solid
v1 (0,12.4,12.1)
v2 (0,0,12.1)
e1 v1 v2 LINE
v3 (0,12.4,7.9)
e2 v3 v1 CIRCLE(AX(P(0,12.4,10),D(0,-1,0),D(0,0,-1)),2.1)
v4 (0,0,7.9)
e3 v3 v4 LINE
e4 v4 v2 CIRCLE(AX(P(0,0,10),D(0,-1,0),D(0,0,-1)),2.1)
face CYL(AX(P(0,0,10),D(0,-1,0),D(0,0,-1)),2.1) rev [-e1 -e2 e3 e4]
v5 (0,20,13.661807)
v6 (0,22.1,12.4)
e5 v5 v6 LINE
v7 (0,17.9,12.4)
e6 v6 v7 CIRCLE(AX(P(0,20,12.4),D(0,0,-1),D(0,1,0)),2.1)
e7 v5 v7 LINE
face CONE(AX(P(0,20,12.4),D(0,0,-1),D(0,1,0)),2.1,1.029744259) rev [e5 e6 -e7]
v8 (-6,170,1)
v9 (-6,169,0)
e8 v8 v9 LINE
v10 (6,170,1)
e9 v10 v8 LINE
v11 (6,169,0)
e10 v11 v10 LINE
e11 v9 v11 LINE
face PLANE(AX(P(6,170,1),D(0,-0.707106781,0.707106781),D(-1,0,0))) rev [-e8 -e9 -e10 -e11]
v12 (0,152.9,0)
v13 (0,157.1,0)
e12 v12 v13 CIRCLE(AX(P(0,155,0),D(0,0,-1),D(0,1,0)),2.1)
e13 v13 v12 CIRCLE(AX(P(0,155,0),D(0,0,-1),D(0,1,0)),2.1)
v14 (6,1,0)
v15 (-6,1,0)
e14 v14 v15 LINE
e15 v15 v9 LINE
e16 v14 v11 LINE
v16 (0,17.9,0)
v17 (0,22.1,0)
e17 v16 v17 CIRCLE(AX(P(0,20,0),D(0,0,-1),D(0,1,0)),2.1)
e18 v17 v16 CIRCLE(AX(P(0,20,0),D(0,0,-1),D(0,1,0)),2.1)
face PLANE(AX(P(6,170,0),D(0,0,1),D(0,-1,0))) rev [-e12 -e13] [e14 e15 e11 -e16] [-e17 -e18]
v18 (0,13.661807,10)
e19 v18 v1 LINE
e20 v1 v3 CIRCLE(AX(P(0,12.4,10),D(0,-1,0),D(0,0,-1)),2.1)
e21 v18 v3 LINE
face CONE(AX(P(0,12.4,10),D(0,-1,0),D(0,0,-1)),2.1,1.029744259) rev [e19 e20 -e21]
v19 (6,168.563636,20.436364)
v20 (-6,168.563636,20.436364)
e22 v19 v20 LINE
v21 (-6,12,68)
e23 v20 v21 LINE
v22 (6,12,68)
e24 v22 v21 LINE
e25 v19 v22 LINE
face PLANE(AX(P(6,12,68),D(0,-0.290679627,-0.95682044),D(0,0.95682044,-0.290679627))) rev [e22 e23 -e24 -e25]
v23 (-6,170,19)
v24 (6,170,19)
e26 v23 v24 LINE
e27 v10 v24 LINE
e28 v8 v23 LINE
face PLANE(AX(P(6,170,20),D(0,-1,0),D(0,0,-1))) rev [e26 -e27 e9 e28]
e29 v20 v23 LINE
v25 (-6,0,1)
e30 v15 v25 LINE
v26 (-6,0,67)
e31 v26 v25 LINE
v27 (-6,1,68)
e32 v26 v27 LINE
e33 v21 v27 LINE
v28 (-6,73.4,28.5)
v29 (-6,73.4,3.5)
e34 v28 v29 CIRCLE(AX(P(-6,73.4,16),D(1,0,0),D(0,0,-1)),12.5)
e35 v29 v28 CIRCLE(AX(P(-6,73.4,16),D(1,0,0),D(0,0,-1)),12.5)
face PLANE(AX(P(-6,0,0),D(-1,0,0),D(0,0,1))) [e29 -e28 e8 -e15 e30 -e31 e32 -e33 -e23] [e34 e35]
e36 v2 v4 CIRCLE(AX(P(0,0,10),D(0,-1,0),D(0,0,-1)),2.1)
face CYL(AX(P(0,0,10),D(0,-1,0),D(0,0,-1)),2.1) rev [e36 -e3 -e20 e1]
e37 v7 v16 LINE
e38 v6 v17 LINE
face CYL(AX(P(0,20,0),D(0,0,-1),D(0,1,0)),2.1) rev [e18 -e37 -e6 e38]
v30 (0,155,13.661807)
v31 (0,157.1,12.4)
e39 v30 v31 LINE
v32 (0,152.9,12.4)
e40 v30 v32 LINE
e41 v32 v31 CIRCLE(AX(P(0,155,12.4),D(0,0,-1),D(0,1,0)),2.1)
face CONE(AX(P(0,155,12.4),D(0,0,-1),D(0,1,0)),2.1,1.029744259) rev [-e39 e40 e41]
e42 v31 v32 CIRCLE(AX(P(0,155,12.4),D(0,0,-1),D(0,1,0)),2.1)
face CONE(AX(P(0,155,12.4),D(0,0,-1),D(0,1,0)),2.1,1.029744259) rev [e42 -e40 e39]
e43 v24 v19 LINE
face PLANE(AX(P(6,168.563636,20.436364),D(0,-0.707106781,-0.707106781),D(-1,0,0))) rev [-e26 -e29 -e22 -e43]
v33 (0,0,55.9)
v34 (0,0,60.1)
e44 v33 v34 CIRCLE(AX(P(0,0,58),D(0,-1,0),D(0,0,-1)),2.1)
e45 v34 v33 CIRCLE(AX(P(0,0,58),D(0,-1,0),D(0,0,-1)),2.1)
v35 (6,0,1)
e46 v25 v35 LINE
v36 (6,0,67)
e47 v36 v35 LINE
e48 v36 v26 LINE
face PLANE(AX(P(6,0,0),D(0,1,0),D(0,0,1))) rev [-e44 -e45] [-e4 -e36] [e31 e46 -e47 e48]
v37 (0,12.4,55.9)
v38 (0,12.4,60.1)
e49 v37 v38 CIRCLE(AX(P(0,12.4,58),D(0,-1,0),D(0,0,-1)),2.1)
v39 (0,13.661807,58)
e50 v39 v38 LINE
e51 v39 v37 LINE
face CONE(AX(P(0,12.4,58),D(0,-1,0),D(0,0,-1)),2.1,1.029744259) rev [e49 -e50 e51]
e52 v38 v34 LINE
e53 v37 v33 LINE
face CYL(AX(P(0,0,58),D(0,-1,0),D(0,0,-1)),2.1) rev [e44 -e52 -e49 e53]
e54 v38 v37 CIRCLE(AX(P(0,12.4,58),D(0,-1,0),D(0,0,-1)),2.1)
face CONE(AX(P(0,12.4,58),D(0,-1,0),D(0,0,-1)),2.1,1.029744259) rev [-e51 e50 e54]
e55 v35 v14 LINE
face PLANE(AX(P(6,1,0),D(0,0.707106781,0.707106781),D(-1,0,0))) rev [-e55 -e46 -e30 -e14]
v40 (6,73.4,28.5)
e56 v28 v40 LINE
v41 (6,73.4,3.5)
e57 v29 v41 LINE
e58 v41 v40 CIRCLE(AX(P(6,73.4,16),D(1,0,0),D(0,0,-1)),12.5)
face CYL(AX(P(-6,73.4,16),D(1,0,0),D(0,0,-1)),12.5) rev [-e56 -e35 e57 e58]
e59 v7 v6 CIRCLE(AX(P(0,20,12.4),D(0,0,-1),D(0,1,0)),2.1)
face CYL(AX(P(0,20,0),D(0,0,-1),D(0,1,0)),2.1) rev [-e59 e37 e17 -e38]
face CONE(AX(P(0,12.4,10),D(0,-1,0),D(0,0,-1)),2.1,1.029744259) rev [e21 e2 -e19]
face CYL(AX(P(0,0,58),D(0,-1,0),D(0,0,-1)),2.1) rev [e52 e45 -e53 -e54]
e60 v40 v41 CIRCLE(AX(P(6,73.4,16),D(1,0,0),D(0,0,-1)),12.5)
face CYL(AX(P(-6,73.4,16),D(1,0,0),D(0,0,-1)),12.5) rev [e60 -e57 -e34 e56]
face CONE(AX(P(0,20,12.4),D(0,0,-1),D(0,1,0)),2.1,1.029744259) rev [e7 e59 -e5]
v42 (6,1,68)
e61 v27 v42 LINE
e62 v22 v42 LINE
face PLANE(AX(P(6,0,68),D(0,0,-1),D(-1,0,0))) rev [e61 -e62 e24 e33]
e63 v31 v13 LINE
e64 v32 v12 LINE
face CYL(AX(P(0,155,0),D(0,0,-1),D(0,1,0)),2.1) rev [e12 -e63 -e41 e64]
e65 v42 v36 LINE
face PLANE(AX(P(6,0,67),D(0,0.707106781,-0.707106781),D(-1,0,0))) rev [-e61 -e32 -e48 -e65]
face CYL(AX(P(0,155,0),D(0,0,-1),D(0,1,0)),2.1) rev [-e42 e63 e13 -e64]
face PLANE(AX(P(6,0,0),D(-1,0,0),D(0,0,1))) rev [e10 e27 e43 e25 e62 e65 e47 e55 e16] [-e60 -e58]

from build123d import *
from OCP.BRepFilletAPI import BRepFilletAPI_MakeChamfer

# Parameters (mm, degrees)
BOSS_EXTRUDE1_DEPTH   = 6
M5_TAPPED_HOLE1_D     = 4.2
M5_TAPPED_HOLE1_DEPTH = 12.4
M5_TAPPED_HOLE1_TIP   = 1.2618073
M5_TAPPED_HOLE2_D     = 4.2
M5_TAPPED_HOLE2_DEPTH = 12.4
M5_TAPPED_HOLE2_TIP   = 1.2618073
CHAMFER1_SIZE         = 1
CHAMFER1_SIZE2        = 1.501184106
SKETCH6_R             = 12.5
CUT_EXTRUDE1_DEPTH    = 184.488419253


with BuildPart() as part:
    # Sketch1 → Boss-Extrude1 (new, symmetric)
    with BuildSketch(Plane(origin=(0, 0, 0), x_dir=(0, 0, -1), z_dir=(1, 0, 0))):
        Polygon((0, 0), (-68, 0), (-68, 12), (-20, 170), (0, 170), align=None)
    extrude(amount=BOSS_EXTRUDE1_DEPTH, both=True)

    # M5 Tapped Hole1
    with Locations(Plane(origin=(0, 0, 0), x_dir=(-1, 0, 0), z_dir=(0, 0, -1))):
        with Locations((0, 20), (0, 155)):
            Hole(M5_TAPPED_HOLE1_D / 2, depth=M5_TAPPED_HOLE1_DEPTH)
            with Locations((0, 0, -(M5_TAPPED_HOLE1_DEPTH + M5_TAPPED_HOLE1_TIP / 2))):  # 118° drill point
                Cone(0, M5_TAPPED_HOLE1_D / 2, M5_TAPPED_HOLE1_TIP, mode=Mode.SUBTRACT)

    # M5 Tapped Hole2
    with Locations(Plane(origin=(0, 0, 0), x_dir=(-1, 0, 0), z_dir=(0, -1, 0))):
        with Locations((0, -58), (0, -10)):
            Hole(M5_TAPPED_HOLE2_D / 2, depth=M5_TAPPED_HOLE2_DEPTH)
            with Locations((0, 0, -(M5_TAPPED_HOLE2_DEPTH + M5_TAPPED_HOLE2_TIP / 2))):  # 118° drill point
                Cone(0, M5_TAPPED_HOLE2_D / 2, M5_TAPPED_HOLE2_TIP, mode=Mode.SUBTRACT)

    # Chamfer1: one chamfer whose edges measure the first distance from different faces: ONE call of the kernel's chamfer builder (chamfer() names one face for all edges)
    chamfer1_edges_1 = [part.edges().sort_by_distance(p)[0] for p in [
        (0, 0, 0),
        (0, 0, 68),
        (0, 170, 0),
    ]]
    chamfer1_edges_2 = [part.edges().sort_by_distance(p)[0] for p in [
        (0, 170, 20),
    ]]
    chamfer1_side_2 = [part.faces().sort_by_distance(p)[0] for p in [
        (0, 170, 10),
    ]]
    chamfer1 = BRepFilletAPI_MakeChamfer(part.part.solid().wrapped)
    for e in chamfer1_edges_1:
        chamfer1.Add(CHAMFER1_SIZE, e.wrapped)
    for e in chamfer1_edges_2:
        chamfer1.Add(CHAMFER1_SIZE, CHAMFER1_SIZE2, e.wrapped, chamfer1_side_2[0].wrapped)  # the first distance lies on this face
    add(Compound.cast(chamfer1.Shape()), mode=Mode.REPLACE)

    # Sketch6 → Cut-Extrude1 (cut, through all)
    with BuildSketch(Plane(origin=(6, 0, 0), x_dir=(0, 0, -1), z_dir=(1, 0, 0))):
        with Locations((-16, 73.4)):
            Circle(SKETCH6_R)
    extrude(amount=-CUT_EXTRUDE1_DEPTH, mode=Mode.SUBTRACT)


solid = part.part
